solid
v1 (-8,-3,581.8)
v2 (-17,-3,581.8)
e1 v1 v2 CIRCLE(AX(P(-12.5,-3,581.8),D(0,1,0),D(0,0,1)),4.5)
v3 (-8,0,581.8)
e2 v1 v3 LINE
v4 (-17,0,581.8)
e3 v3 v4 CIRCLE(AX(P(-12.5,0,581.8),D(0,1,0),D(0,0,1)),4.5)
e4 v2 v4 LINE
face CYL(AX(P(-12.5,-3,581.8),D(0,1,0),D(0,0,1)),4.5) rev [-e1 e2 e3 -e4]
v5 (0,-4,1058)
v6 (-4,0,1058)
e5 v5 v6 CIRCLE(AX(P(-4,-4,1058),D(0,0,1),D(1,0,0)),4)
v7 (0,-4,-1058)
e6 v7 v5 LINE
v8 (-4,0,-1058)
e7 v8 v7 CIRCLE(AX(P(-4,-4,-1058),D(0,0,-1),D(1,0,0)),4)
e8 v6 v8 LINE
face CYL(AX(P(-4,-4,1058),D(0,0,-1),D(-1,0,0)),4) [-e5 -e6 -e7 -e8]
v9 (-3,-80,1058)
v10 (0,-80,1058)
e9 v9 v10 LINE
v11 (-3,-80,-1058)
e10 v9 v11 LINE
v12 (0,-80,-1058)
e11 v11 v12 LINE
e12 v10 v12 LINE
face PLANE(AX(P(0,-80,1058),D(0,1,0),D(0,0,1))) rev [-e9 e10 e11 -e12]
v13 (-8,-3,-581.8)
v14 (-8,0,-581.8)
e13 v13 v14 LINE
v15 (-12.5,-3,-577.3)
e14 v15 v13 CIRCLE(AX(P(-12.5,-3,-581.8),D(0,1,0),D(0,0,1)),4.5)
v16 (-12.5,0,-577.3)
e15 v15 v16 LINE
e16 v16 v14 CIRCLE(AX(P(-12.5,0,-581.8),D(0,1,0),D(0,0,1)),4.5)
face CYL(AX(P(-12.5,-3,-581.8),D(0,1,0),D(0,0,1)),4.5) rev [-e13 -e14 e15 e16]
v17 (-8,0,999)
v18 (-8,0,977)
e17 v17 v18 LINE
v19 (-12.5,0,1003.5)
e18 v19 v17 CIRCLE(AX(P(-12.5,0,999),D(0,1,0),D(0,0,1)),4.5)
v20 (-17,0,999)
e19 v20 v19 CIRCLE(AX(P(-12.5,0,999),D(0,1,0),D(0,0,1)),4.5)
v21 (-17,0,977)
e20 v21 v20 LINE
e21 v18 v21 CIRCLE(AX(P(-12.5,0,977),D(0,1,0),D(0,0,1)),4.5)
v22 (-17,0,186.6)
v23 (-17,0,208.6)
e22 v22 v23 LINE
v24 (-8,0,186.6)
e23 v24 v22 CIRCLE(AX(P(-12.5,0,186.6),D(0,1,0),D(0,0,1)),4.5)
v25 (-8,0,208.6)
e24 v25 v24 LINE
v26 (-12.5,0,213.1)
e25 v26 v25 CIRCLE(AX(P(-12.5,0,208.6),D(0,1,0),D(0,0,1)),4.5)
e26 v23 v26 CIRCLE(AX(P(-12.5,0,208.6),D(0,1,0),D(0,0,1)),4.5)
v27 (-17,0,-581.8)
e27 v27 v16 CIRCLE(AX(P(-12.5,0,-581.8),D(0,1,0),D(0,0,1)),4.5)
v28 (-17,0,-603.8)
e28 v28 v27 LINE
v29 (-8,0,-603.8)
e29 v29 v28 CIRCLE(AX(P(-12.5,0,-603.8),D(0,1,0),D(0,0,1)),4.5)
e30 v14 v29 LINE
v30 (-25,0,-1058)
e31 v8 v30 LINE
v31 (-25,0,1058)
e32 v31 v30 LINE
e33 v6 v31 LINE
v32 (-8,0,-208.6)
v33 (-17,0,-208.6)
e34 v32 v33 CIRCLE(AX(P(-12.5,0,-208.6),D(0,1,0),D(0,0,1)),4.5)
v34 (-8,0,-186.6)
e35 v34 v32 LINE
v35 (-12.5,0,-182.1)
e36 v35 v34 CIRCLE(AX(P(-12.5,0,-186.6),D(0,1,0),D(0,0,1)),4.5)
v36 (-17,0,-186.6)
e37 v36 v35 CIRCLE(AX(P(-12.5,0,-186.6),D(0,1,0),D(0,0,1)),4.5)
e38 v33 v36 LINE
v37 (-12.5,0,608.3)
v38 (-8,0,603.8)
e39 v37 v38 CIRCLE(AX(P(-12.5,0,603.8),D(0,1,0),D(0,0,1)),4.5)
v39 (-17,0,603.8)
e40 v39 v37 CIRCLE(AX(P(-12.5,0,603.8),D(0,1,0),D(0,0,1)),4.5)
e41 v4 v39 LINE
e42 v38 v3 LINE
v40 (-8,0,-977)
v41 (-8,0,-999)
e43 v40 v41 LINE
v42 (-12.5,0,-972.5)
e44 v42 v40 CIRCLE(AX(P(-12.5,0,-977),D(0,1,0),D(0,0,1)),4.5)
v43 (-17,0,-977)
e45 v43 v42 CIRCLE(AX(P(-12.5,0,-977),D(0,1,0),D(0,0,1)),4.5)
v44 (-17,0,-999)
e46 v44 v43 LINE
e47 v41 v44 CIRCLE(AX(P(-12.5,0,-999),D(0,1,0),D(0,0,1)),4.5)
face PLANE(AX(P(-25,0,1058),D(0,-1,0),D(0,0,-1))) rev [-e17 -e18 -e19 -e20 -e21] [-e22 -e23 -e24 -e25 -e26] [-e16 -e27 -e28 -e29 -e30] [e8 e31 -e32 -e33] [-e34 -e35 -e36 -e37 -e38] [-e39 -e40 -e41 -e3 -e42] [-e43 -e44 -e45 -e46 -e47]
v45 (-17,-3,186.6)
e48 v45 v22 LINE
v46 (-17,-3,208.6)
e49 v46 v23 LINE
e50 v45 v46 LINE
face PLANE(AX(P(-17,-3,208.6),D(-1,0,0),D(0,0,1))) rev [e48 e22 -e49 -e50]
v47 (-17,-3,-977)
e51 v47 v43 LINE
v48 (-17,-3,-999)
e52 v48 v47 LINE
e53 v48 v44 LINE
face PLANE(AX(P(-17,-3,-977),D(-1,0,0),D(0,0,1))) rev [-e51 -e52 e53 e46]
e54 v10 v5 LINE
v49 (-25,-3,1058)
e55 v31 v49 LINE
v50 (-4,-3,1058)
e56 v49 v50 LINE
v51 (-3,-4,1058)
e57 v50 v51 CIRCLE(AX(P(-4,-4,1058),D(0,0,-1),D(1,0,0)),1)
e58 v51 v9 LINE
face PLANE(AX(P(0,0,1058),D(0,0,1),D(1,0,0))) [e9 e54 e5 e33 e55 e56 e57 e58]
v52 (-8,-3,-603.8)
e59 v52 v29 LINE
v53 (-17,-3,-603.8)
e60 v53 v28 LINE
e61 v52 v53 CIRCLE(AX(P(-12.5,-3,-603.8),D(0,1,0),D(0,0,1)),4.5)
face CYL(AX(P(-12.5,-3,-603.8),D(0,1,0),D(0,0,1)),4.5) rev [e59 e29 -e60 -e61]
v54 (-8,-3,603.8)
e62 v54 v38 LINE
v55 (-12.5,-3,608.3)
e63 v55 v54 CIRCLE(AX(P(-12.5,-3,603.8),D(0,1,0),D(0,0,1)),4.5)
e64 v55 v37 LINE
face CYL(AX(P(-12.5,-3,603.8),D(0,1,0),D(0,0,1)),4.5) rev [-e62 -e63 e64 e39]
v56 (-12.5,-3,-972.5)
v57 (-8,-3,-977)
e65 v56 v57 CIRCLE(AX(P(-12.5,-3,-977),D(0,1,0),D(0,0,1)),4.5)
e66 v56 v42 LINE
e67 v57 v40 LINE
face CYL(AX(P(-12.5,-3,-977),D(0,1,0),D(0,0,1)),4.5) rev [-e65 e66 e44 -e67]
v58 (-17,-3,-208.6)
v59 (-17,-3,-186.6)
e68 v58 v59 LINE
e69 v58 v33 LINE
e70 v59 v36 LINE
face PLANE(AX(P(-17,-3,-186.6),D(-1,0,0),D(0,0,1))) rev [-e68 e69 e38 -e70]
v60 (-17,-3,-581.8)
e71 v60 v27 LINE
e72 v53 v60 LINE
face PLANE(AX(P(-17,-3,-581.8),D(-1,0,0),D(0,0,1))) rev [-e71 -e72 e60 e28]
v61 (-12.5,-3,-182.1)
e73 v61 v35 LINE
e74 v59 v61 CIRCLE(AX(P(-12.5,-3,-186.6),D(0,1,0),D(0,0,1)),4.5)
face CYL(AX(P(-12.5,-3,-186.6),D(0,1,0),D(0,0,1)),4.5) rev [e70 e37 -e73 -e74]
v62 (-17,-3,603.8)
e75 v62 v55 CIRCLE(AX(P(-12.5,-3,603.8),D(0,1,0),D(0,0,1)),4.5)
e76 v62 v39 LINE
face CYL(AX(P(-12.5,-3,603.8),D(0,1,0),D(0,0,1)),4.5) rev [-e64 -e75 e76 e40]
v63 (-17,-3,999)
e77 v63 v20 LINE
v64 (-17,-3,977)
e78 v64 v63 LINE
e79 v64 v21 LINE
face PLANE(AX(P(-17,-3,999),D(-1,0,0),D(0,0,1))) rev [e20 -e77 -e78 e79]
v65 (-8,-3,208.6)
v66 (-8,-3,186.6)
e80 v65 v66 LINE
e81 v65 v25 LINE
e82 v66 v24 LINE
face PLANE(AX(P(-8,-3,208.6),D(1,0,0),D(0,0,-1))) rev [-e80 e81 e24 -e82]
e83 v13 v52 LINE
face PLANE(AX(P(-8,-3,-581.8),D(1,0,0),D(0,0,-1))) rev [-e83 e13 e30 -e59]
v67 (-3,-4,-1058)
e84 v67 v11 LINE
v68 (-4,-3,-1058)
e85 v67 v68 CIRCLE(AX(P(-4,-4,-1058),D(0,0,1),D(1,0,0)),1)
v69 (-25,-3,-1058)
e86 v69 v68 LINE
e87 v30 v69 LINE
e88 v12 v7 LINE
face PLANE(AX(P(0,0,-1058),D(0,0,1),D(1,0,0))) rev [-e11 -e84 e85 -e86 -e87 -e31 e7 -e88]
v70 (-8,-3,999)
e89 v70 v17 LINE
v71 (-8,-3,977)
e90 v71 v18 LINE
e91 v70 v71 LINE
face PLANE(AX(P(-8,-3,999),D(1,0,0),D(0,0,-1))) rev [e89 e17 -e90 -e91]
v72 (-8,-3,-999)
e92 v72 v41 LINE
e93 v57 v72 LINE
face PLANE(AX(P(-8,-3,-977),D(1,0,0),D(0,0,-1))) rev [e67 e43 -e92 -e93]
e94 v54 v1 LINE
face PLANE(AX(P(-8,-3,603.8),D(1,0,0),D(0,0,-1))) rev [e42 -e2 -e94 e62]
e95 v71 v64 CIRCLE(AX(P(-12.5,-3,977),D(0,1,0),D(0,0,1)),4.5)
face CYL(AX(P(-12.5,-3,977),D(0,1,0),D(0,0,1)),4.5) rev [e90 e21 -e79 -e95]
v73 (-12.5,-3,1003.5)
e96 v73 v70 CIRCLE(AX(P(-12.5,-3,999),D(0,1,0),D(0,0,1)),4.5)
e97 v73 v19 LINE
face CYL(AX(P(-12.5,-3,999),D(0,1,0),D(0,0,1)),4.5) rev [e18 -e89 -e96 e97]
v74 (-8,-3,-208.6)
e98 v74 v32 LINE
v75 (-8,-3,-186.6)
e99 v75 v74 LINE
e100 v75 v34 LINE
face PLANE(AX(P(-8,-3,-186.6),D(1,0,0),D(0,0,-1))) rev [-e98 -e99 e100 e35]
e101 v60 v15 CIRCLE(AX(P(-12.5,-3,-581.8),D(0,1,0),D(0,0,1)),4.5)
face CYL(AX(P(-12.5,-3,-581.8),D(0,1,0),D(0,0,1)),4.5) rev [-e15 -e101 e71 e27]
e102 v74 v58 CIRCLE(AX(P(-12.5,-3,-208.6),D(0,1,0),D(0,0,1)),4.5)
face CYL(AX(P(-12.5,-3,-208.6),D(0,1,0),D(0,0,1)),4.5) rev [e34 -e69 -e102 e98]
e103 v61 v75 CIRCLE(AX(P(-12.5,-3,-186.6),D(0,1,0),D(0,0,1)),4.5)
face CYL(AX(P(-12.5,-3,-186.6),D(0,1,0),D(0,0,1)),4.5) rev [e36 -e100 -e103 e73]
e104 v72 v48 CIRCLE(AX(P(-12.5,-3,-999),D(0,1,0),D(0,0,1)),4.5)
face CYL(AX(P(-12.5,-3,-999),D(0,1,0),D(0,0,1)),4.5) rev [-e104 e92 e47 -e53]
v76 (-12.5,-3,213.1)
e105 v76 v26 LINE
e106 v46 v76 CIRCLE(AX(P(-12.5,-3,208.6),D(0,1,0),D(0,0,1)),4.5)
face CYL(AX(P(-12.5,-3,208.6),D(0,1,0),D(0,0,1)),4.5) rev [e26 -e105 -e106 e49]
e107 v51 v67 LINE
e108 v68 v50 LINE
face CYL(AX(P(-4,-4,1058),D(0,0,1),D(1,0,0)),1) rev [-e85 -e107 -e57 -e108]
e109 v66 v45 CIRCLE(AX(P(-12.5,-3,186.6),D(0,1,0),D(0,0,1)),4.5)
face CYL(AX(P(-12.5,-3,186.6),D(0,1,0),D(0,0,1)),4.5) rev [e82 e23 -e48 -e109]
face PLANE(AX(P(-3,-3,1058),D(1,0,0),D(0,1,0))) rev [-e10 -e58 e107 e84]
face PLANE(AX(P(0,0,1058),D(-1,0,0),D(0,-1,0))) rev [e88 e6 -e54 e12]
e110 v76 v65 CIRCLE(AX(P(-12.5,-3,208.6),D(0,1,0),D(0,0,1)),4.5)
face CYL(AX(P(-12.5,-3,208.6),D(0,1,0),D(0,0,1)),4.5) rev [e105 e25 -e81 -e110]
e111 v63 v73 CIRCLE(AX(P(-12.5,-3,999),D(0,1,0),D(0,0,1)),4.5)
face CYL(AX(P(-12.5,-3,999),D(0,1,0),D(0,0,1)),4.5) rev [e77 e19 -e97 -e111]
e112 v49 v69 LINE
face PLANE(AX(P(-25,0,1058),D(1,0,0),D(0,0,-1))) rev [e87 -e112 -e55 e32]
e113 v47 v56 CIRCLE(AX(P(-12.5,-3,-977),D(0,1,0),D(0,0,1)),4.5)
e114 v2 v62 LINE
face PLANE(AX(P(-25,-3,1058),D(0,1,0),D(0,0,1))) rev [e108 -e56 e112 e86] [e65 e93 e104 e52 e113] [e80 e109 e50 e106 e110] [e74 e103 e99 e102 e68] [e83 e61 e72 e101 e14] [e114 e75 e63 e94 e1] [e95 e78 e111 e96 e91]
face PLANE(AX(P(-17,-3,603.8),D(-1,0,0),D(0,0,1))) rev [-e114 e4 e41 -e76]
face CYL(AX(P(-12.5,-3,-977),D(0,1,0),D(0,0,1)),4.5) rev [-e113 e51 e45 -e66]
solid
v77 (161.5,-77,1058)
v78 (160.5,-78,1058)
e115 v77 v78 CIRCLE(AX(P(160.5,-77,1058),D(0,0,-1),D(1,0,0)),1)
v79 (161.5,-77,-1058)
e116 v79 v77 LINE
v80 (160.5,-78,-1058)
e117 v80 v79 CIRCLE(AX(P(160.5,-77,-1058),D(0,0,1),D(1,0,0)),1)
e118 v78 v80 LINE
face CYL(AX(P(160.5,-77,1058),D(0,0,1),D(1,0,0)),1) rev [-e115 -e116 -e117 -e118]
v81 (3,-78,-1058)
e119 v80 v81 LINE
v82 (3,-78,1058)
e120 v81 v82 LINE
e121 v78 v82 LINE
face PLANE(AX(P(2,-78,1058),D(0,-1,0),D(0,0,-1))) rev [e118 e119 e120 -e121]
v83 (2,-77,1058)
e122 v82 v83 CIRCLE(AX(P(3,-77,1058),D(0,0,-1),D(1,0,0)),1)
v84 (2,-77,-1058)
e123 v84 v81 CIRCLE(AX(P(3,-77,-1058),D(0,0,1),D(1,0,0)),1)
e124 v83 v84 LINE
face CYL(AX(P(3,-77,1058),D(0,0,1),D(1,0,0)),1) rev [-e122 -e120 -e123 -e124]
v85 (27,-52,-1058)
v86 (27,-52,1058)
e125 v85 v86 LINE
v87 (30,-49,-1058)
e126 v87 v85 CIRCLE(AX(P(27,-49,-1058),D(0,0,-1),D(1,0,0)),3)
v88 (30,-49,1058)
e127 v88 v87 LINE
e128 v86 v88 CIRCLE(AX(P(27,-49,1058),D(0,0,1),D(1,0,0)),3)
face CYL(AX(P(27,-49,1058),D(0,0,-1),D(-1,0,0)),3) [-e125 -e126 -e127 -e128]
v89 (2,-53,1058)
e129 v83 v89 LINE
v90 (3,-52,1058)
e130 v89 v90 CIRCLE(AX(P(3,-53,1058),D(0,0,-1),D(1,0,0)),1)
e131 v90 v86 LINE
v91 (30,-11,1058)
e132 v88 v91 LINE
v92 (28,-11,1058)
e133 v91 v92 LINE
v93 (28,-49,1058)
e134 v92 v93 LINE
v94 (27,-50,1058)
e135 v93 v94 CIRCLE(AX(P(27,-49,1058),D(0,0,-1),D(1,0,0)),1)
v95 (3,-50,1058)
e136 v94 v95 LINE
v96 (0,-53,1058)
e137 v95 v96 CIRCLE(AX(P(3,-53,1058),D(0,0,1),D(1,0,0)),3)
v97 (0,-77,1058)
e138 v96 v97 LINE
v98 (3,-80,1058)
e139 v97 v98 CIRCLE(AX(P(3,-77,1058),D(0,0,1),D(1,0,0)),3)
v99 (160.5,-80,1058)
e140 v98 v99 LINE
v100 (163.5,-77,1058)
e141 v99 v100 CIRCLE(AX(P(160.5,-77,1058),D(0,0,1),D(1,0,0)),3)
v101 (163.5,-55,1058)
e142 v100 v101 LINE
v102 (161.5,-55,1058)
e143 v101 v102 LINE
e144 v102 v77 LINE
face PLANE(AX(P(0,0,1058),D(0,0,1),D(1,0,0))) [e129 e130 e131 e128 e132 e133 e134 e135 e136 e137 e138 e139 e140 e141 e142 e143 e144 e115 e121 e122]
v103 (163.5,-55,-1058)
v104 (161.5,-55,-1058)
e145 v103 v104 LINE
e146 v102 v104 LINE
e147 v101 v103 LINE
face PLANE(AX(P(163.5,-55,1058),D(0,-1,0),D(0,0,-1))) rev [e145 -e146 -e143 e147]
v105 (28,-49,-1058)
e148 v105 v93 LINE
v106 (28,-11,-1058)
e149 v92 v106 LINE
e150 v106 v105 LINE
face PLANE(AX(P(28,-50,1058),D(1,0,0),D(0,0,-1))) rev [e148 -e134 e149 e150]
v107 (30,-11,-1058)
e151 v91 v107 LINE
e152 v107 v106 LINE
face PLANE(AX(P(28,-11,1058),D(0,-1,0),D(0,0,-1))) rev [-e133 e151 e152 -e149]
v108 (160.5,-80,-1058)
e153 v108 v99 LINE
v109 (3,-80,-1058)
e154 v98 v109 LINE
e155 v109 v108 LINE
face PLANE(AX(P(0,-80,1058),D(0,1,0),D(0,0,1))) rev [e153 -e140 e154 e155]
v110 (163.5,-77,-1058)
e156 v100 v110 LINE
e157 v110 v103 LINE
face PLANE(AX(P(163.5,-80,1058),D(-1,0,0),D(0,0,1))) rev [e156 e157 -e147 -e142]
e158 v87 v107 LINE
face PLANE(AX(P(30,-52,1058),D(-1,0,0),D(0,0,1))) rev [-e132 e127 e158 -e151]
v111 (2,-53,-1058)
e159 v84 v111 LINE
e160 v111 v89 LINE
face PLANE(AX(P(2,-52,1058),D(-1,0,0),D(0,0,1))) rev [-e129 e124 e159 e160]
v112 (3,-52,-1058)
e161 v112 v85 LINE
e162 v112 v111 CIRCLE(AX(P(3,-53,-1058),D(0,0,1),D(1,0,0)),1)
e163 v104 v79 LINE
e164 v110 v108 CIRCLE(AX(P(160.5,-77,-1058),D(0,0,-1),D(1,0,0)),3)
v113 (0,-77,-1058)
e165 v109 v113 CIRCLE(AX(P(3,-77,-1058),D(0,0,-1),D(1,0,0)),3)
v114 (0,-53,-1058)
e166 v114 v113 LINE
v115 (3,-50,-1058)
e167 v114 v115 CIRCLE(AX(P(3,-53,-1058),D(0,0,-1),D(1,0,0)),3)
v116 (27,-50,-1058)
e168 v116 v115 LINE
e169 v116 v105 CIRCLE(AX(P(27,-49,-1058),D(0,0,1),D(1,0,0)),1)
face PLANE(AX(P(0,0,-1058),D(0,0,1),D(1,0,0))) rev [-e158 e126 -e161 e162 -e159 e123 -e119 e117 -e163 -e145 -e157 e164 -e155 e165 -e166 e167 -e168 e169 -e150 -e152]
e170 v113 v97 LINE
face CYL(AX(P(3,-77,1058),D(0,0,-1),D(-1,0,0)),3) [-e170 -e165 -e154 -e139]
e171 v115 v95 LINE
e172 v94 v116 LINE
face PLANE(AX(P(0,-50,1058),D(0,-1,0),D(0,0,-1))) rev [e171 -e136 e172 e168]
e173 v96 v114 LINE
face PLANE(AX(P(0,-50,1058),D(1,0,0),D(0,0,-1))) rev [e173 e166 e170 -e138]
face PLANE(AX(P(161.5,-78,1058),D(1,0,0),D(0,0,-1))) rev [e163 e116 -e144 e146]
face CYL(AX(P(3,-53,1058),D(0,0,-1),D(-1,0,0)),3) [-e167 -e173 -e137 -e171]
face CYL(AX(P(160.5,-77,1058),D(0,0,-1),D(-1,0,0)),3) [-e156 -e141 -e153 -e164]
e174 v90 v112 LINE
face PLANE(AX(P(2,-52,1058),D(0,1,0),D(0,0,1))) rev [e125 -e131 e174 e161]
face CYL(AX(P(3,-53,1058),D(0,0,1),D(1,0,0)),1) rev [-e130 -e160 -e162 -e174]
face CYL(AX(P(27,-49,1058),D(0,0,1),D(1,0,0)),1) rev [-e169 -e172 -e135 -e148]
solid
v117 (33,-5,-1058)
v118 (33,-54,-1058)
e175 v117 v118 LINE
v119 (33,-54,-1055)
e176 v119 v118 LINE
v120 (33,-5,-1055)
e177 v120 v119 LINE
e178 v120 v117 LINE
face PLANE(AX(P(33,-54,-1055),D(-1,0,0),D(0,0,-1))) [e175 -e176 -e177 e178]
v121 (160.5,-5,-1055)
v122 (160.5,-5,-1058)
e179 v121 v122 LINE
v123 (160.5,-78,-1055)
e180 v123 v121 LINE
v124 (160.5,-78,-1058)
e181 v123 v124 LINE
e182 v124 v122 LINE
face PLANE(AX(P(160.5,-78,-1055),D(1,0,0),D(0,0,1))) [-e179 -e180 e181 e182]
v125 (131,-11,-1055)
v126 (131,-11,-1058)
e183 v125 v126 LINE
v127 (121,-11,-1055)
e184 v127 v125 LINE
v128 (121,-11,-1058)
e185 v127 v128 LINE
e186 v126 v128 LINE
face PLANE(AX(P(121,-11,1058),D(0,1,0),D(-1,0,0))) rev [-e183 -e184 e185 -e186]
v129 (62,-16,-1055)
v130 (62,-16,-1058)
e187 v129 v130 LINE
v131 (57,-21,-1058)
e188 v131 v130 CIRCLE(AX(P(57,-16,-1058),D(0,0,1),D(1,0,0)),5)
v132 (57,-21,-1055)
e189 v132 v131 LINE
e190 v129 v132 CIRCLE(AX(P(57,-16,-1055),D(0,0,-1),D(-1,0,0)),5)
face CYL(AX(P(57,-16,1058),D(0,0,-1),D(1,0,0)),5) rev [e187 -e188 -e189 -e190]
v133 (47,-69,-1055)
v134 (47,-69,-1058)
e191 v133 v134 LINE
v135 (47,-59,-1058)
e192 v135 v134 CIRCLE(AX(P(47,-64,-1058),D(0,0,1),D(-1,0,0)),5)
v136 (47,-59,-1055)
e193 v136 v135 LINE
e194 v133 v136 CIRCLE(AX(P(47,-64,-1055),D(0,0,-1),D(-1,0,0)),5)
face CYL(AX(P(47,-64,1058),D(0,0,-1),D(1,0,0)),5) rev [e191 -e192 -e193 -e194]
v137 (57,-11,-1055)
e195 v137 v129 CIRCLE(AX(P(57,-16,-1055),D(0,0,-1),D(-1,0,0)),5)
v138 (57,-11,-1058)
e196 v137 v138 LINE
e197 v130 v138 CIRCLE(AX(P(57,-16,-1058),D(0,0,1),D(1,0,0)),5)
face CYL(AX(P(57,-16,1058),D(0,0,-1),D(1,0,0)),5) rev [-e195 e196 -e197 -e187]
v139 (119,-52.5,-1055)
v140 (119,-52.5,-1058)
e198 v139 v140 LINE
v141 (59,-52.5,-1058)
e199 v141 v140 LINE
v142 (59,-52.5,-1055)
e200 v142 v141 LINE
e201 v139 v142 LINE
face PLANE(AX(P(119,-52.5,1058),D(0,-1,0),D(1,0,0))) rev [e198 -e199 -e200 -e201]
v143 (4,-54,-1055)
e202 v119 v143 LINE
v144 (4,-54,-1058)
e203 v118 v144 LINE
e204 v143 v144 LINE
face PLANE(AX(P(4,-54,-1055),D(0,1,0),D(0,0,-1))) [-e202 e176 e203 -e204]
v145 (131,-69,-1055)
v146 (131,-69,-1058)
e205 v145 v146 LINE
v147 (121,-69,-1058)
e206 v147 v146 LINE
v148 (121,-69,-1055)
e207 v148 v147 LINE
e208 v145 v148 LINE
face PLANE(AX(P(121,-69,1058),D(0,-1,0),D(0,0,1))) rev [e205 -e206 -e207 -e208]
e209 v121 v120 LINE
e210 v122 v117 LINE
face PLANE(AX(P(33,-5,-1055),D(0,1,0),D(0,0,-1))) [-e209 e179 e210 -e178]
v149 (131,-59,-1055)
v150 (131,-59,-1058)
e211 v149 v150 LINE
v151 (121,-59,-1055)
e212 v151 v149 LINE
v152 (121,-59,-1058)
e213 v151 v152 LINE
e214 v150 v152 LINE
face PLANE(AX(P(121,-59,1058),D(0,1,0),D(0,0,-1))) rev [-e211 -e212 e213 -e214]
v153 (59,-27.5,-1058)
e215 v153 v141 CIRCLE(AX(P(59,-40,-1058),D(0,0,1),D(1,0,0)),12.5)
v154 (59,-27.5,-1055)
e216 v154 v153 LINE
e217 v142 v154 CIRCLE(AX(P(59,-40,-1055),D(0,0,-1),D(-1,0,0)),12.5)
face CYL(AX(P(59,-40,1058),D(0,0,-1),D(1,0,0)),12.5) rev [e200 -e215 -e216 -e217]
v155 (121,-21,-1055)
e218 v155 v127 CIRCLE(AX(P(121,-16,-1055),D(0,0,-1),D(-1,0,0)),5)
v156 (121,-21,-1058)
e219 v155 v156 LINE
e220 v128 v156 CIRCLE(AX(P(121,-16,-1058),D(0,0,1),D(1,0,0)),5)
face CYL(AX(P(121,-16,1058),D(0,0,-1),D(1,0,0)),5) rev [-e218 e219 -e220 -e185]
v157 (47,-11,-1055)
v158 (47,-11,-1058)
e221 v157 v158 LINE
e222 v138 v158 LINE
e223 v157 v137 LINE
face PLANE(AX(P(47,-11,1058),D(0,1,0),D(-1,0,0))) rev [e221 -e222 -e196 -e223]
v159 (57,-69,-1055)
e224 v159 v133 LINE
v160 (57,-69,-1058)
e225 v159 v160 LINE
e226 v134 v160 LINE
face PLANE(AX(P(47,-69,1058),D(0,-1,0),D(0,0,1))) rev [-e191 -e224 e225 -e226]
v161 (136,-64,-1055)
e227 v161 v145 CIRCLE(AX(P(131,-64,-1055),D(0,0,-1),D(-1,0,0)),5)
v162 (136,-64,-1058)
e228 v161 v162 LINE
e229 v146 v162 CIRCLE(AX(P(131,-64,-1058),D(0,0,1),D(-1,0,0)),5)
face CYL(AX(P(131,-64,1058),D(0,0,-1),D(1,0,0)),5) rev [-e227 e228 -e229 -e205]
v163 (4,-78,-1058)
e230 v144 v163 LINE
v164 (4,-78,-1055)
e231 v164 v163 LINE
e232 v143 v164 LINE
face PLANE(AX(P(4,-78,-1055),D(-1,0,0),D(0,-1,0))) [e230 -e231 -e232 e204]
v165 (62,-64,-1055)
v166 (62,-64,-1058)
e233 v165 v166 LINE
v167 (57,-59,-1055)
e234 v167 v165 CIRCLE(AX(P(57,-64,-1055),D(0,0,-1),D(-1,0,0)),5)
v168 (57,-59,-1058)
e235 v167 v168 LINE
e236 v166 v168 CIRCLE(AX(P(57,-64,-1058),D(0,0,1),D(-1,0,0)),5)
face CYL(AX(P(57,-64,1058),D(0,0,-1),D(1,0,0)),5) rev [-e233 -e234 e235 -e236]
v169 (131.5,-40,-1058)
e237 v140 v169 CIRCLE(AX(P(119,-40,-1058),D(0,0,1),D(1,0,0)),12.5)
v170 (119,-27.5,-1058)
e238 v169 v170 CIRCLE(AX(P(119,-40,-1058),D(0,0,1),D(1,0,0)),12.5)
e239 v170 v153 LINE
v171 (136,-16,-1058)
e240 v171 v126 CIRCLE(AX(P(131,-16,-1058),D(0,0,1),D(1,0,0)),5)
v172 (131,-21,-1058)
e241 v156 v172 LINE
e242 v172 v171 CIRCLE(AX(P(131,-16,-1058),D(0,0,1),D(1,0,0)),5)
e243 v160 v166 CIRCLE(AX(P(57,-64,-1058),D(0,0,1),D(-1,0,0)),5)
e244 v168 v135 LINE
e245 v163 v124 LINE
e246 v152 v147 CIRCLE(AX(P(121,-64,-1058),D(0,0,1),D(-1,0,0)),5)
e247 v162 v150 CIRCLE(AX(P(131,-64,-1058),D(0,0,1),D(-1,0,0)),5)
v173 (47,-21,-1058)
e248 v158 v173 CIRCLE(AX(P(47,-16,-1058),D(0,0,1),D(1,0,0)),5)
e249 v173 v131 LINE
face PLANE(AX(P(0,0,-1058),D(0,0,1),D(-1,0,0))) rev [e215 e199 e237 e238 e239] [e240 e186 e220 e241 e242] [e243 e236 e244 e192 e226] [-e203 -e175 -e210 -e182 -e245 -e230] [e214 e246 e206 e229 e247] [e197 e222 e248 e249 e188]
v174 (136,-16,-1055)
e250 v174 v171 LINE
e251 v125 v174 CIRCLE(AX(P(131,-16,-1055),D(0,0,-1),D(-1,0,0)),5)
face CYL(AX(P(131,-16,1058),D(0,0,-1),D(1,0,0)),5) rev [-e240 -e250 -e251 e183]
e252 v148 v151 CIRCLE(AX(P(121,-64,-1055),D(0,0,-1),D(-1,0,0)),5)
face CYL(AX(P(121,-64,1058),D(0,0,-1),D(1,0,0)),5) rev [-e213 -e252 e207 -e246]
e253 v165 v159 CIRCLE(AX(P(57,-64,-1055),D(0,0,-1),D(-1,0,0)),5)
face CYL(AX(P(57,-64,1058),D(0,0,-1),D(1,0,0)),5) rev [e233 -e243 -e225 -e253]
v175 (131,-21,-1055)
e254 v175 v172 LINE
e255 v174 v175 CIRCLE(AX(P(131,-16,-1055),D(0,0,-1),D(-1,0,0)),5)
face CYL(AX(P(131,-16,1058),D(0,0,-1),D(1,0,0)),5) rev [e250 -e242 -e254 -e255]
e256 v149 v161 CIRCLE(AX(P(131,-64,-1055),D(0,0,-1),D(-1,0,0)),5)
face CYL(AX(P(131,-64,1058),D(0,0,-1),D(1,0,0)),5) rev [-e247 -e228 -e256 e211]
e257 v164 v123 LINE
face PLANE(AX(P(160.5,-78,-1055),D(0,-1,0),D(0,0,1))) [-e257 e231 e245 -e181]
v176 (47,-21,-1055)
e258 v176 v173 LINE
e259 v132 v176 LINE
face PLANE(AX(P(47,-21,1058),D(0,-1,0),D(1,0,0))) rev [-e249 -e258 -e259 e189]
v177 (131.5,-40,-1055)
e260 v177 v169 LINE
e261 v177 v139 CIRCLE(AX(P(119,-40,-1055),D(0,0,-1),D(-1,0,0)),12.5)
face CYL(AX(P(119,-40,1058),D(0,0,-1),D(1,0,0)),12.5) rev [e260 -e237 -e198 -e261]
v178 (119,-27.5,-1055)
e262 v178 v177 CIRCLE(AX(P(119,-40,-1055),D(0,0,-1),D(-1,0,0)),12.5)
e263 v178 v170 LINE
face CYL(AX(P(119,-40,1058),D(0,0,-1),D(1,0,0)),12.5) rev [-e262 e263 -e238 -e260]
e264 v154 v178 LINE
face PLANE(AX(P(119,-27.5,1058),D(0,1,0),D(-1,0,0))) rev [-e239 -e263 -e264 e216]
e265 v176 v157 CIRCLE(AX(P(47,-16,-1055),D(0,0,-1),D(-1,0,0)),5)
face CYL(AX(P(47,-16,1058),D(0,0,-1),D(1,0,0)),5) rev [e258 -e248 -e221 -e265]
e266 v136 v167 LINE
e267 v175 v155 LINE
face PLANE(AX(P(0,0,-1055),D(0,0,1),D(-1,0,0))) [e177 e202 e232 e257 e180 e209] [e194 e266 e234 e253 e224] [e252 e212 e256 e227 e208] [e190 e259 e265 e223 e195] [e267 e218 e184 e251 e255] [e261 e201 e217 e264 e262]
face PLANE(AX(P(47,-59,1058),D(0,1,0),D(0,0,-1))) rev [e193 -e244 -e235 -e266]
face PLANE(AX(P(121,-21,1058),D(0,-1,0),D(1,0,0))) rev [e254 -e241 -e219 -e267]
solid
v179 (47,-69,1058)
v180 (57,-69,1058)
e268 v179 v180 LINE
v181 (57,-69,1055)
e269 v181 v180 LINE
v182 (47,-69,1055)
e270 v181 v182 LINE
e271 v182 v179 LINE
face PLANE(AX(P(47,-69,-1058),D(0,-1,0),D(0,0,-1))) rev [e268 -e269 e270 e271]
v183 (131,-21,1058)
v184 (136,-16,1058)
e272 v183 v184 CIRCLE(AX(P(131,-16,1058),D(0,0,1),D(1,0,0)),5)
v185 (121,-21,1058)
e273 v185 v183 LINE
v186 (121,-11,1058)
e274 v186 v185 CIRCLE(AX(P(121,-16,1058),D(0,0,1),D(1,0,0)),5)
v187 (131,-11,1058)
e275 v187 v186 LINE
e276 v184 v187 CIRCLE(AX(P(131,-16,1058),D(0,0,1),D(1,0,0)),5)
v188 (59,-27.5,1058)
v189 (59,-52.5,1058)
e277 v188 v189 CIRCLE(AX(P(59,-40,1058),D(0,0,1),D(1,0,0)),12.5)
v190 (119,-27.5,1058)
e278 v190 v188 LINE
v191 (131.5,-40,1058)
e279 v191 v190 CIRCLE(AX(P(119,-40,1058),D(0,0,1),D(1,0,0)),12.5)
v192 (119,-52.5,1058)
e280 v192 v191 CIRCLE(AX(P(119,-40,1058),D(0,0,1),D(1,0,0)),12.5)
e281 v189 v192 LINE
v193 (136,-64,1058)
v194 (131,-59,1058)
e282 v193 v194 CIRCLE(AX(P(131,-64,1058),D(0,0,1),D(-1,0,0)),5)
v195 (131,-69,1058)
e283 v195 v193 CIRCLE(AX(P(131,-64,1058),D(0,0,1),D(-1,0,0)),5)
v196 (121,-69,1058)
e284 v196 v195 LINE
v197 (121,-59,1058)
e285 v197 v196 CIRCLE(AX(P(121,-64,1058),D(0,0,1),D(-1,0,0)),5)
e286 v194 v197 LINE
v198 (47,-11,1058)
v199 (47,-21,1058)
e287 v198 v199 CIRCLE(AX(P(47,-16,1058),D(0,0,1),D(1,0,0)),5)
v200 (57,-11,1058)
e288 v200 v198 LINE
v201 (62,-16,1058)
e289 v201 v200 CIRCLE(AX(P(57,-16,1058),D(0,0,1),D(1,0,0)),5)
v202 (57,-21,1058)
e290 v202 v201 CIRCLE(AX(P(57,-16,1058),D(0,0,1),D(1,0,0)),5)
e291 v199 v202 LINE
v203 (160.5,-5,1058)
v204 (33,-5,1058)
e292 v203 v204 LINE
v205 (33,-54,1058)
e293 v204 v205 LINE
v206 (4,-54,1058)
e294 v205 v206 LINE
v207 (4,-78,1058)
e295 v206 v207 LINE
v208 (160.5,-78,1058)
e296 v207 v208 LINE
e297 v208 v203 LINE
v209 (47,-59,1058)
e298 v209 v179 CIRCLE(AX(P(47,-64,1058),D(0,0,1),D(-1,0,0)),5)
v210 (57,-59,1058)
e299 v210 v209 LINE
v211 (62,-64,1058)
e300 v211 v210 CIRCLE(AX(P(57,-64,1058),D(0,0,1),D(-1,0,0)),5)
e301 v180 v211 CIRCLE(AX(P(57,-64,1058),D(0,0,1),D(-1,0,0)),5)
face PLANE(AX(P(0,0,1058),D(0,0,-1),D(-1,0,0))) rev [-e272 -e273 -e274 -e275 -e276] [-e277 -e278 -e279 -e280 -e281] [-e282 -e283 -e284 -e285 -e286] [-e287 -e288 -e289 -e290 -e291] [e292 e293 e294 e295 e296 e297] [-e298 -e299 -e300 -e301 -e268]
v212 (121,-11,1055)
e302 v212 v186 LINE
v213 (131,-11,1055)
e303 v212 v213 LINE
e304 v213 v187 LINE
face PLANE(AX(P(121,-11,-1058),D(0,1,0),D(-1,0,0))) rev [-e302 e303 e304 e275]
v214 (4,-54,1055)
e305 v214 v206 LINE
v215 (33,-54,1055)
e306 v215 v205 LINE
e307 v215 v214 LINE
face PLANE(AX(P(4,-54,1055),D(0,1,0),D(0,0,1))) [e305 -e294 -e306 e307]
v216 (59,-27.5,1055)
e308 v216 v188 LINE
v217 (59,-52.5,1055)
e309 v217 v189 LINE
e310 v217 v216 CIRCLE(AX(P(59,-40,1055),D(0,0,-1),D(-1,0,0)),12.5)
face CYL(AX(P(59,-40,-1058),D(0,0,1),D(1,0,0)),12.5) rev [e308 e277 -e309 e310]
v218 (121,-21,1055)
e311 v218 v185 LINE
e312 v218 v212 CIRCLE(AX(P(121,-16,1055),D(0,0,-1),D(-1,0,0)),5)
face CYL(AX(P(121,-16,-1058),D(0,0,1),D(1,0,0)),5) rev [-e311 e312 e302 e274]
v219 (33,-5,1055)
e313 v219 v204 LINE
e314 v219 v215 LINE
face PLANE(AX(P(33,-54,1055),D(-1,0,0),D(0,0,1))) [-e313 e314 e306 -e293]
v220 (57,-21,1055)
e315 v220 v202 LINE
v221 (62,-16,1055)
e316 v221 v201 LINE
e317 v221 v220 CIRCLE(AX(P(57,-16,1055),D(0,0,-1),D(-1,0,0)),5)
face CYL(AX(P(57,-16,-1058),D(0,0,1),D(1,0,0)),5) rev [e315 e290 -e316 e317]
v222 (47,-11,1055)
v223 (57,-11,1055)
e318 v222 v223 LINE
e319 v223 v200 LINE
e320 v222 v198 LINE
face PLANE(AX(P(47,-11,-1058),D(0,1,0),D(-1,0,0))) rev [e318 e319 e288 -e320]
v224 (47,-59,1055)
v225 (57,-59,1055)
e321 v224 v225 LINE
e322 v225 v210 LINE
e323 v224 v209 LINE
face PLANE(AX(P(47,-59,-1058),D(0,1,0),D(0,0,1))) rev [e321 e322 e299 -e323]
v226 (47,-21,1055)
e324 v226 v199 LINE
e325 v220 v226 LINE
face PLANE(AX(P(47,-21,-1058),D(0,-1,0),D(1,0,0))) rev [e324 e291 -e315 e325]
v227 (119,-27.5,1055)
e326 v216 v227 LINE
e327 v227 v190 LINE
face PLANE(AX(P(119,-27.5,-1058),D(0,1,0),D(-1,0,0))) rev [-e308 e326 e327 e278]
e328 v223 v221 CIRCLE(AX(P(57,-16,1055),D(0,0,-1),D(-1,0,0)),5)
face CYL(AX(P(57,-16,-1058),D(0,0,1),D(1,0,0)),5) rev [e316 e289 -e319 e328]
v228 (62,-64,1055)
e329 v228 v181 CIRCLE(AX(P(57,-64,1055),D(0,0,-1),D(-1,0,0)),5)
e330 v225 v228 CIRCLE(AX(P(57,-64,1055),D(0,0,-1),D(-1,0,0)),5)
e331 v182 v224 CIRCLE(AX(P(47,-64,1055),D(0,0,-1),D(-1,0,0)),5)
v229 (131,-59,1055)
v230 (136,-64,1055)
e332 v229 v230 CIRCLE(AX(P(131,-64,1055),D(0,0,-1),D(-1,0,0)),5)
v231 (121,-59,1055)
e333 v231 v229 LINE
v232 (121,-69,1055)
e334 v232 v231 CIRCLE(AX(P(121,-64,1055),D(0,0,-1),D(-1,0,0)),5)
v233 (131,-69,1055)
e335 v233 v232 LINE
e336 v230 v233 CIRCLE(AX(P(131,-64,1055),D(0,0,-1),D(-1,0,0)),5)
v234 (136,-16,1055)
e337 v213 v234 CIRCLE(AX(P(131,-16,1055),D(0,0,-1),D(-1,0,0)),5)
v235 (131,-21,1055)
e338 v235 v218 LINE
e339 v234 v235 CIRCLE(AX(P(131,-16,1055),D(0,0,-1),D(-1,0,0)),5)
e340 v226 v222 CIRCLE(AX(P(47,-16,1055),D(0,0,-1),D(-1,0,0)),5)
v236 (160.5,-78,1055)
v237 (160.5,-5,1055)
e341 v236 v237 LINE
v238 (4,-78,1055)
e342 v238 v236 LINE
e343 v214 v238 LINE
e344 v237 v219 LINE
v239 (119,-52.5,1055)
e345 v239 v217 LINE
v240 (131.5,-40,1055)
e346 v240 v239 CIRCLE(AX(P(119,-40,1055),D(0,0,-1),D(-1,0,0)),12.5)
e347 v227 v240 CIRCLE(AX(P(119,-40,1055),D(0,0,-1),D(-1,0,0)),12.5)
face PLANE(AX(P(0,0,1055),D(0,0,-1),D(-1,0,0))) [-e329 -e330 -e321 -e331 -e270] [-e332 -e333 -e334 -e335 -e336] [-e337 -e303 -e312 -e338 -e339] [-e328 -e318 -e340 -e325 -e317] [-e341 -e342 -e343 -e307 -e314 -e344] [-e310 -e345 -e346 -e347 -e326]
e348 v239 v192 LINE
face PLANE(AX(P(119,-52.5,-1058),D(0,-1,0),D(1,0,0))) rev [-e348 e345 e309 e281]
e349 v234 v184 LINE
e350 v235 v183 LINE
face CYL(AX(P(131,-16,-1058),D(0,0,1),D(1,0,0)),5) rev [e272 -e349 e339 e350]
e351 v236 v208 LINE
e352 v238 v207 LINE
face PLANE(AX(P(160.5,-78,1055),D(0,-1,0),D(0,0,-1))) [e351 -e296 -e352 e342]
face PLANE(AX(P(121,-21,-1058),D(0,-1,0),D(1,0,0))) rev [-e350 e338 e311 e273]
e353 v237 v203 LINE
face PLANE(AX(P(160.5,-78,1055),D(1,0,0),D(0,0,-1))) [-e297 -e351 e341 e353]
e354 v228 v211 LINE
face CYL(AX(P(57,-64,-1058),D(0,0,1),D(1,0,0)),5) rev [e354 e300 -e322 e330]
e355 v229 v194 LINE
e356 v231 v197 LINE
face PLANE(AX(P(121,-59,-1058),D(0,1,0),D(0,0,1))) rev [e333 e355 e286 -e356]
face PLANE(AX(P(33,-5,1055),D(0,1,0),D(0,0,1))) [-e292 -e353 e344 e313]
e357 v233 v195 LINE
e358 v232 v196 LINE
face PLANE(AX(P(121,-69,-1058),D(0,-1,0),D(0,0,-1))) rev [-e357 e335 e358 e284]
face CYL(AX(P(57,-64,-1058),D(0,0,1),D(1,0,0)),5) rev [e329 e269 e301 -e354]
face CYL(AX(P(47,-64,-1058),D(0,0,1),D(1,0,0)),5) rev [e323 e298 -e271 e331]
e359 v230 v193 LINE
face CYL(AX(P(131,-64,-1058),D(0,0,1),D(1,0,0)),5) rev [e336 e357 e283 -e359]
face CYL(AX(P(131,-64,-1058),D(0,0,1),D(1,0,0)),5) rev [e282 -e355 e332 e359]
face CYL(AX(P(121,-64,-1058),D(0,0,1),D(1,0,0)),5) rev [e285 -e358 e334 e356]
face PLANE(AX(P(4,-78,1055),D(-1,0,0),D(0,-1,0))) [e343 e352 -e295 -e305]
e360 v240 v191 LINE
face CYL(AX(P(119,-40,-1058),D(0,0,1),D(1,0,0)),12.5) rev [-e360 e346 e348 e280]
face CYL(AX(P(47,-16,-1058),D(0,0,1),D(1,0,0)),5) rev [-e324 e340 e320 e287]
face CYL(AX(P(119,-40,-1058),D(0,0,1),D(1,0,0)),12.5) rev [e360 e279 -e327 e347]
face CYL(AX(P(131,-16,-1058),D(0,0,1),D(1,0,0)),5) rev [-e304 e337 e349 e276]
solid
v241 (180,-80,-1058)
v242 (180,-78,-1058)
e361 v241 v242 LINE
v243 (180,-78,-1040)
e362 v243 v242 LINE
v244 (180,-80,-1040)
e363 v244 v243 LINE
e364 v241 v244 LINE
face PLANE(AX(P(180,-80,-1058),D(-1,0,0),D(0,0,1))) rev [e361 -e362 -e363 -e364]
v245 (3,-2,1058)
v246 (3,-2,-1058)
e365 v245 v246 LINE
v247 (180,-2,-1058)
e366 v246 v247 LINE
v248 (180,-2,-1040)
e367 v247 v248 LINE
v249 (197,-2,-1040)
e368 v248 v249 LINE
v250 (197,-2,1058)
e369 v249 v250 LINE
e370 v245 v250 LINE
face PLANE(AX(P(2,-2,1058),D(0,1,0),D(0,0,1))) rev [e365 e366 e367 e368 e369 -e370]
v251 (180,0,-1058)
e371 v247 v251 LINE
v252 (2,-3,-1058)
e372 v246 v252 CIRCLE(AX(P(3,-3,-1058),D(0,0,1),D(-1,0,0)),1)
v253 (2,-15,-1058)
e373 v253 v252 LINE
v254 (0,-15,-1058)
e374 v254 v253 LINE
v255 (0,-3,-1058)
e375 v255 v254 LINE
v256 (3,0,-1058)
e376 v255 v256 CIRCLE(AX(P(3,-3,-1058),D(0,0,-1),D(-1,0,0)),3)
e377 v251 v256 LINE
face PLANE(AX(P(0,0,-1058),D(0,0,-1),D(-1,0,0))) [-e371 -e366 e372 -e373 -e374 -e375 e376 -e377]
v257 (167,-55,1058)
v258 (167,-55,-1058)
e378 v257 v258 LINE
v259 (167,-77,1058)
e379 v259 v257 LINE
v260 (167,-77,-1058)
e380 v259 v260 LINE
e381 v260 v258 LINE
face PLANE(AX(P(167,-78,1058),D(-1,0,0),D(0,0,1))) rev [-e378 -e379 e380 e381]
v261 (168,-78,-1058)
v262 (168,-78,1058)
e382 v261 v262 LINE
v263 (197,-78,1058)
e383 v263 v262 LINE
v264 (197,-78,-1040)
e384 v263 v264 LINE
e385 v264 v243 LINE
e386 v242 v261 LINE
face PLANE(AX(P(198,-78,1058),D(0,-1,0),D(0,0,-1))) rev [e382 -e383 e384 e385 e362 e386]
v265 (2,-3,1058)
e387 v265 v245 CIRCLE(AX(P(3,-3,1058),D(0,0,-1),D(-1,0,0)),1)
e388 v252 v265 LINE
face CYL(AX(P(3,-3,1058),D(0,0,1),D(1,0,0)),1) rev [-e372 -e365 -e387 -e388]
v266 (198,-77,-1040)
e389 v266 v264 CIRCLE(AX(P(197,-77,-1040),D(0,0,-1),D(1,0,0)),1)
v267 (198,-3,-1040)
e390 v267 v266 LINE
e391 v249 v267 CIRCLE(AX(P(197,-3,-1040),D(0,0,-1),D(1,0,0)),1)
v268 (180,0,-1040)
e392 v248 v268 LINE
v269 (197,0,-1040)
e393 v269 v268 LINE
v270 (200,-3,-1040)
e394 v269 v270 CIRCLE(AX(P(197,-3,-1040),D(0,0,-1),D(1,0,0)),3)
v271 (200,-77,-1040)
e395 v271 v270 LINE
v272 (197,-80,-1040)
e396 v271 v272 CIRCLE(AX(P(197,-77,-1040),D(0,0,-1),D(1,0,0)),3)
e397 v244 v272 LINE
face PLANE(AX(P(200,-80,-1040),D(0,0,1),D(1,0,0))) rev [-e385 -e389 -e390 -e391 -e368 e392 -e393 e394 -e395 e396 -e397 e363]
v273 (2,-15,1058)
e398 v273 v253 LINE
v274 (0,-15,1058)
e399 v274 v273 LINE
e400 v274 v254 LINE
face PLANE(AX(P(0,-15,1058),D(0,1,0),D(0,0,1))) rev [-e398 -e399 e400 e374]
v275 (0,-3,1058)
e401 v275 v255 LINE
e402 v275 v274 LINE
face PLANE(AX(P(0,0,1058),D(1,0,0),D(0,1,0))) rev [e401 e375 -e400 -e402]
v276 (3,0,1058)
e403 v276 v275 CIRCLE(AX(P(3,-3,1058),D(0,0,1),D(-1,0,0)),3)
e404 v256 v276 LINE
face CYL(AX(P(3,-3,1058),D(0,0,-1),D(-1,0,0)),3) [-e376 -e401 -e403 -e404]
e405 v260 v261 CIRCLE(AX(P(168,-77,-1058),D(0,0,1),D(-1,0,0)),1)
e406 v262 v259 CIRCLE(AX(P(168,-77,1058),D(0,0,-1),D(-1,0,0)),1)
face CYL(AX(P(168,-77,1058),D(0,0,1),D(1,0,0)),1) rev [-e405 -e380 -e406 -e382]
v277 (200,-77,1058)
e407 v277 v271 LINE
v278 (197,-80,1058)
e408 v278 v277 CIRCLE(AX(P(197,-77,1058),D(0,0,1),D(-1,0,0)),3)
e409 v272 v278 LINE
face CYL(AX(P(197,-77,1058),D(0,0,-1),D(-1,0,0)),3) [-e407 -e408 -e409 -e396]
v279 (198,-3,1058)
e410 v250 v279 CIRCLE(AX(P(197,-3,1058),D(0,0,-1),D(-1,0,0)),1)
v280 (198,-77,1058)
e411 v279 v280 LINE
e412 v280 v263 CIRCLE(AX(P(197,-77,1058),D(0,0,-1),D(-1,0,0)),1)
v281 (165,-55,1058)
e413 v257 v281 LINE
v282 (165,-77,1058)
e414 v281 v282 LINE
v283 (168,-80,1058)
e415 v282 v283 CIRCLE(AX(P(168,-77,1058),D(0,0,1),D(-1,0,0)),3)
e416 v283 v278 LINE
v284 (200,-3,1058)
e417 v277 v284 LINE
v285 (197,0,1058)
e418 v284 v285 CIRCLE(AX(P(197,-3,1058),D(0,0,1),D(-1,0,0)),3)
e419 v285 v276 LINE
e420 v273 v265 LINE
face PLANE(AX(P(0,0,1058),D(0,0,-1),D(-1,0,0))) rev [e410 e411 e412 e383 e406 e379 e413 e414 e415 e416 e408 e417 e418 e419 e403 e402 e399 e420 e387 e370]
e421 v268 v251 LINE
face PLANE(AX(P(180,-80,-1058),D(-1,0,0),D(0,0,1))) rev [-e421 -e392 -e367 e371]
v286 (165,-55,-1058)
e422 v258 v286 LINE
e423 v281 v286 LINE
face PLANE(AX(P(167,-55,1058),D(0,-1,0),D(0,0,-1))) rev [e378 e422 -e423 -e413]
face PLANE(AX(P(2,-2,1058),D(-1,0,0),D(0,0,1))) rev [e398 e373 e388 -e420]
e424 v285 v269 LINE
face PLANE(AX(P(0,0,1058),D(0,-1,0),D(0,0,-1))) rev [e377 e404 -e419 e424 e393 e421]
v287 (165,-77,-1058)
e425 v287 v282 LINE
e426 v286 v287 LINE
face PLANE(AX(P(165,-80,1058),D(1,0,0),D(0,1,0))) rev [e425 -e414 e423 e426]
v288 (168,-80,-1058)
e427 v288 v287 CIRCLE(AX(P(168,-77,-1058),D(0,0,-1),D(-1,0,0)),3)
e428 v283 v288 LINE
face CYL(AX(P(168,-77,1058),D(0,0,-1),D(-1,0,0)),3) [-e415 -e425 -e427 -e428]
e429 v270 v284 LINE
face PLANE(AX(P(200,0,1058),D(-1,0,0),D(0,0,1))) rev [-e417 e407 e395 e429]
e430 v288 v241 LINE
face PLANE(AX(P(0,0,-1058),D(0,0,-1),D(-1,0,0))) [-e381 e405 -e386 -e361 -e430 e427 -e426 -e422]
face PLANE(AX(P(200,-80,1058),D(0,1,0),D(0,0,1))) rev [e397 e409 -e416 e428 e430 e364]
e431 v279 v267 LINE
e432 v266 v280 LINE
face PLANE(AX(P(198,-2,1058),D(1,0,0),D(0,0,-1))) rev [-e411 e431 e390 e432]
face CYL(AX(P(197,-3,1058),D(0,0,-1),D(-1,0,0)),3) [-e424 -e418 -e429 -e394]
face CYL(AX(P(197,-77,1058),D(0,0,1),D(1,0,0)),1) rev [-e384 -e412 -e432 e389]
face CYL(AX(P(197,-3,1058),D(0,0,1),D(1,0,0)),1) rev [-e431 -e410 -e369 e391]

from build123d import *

# Parameters (mm, degrees)
EXTRUDE_1_DEPTH             = 1058
EXTRUDE_2_DEPTH             = 1058
EXTRUDE_2_2_DEPTH           = 1058
EXTRUDE_3_DEPTH             = 3
FILLET_1_R                  = 4
FILLET_2_R                  = 1
FILLET_3_R                  = 1
FILLET_4_R                  = 1
FILLET_5_R                  = 3
FILLET_6_R                  = 3
CUT_EXTRUDE_1_DEPTH         = 2127.935824138
CUT_EXTRUDE_3490_DEPTH      = 3
CUT_EXTRUDE_3711_DEPTH      = 1080.705515407
CUT_EXTRUDE_3711_DEPTH_BACK = 1080.705515407
SKETCH_6_W                  = 20
SKETCH_6_H                  = 18


with BuildPart() as part:
    # 草图1 → 凸台-拉伸1 (new, symmetric)
    with BuildSketch(Plane.XY):
        Polygon((-25, 0), (0, 0), (0, -80), (-3, -80), (-3, -3), (-25, -3), align=None)
    extrude(amount=EXTRUDE_1_DEPTH, both=True)

    # 圆角1
    fillet_1_edges = [part.edges().sort_by_distance(p)[0] for p in [
        (0, 0, 0),
    ]]
    fillet(fillet_1_edges, radius=FILLET_1_R)

    # 圆角2
    fillet_2_edges = [part.edges().sort_by_distance(p)[0] for p in [
        (-3, -3, 0),
    ]]
    fillet(fillet_2_edges, radius=FILLET_2_R)

    # 草图7 → Cut-Extrude 3490 (cut)
    with BuildSketch(Plane(origin=(0, 0, 0), x_dir=(1, 0, 0), z_dir=(0, 1, 0))):
        with BuildLine():
            Line((-17, 977), (-17, 999))
            ThreePointArc((-17, 999), (-12.5, 1003.5), (-8, 999))
            Line((-8, 999), (-8, 977))
            ThreePointArc((-8, 977), (-12.5, 972.5), (-17, 977))
        make_face()
        with BuildLine():
            Line((-17, 581.8), (-17, 603.8))
            ThreePointArc((-17, 603.8), (-12.5, 608.3), (-8, 603.8))
            Line((-8, 603.8), (-8, 581.8))
            ThreePointArc((-8, 581.8), (-12.5, 577.3), (-17, 581.8))
        make_face()
        with BuildLine():
            Line((-17, 186.6), (-17, 208.6))
            ThreePointArc((-17, 208.6), (-12.5, 213.1), (-8, 208.6))
            Line((-8, 208.6), (-8, 186.6))
            ThreePointArc((-8, 186.6), (-12.5, 182.1), (-17, 186.6))
        make_face()
        with BuildLine():
            Line((-17, -208.6), (-17, -186.6))
            ThreePointArc((-17, -186.6), (-12.5, -182.1), (-8, -186.6))
            Line((-8, -186.6), (-8, -208.6))
            ThreePointArc((-8, -208.6), (-12.5, -213.1), (-17, -208.6))
        make_face()
        with BuildLine():
            Line((-17, -603.8), (-17, -581.8))
            ThreePointArc((-17, -581.8), (-12.5, -577.3), (-8, -581.8))
            Line((-8, -581.8), (-8, -603.8))
            ThreePointArc((-8, -603.8), (-12.5, -608.3), (-17, -603.8))
        make_face()
        with BuildLine():
            Line((-17, -999), (-17, -977))
            ThreePointArc((-17, -977), (-12.5, -972.5), (-8, -977))
            Line((-8, -977), (-8, -999))
            ThreePointArc((-8, -999), (-12.5, -1003.5), (-17, -999))
        make_face()
    extrude(amount=-CUT_EXTRUDE_3490_DEPTH, mode=Mode.SUBTRACT)


with BuildPart() as body_2:
    # 草图2 → 凸台-拉伸2 (new, symmetric)
    with BuildSketch(Plane.XY):
        Polygon((0, 0), (0, -15), (2, -15), (2, -2), (198, -2), (198, -78), (167, -78), (167, -55), (165, -55), (165, -80), (200, -80), (200, 0), align=None)
    extrude(amount=EXTRUDE_2_DEPTH, both=True)

    # 圆角3
    fillet_3_edges = [body_2.edges().sort_by_distance(p)[0] for p in [
        (167, -78, 0),
        (198, -78, 0),
        (198, -2, 0),
        (2, -2, 0),
    ]]
    fillet(fillet_3_edges, radius=FILLET_3_R)

    # 圆角5
    fillet_5_edges = [body_2.edges().sort_by_distance(p)[0] for p in [
        (200, 0, 0),
        (200, -80, 0),
        (165, -80, 0),
        (0, 0, 0),
    ]]
    fillet(fillet_5_edges, radius=FILLET_5_R)

    # 草图6 → Cut-Extrude 3711 (cut, two sides: drawn at the far end of the back side and taken through both)
    with BuildSketch(Plane(origin=(0, 0, 0), x_dir=(1, 0, 0), z_dir=(0, 1, 0)).offset(-CUT_EXTRUDE_3711_DEPTH_BACK)):
        with Locations((190, 1049)):
            Rectangle(SKETCH_6_W, SKETCH_6_H)
    extrude(amount=CUT_EXTRUDE_3711_DEPTH + CUT_EXTRUDE_3711_DEPTH_BACK, mode=Mode.SUBTRACT)


with BuildPart() as body_3:
    # 草图2 → Extrude 2 2 (new, symmetric)
    with BuildSketch(Plane.XY):
        Polygon((0, -50), (0, -80), (163.5, -80), (163.5, -55), (161.5, -55), (161.5, -78), (2, -78), (2, -52), (30, -52), (30, -11), (28, -11), (28, -50), align=None)
    extrude(amount=EXTRUDE_2_2_DEPTH, both=True)

    # 圆角4
    fillet_4_edges = [body_3.edges().sort_by_distance(p)[0] for p in [
        (28, -50, 0),
        (2, -52, 0),
        (2, -78, 0),
        (161.5, -78, 0),
    ]]
    fillet(fillet_4_edges, radius=FILLET_4_R)

    # 圆角6
    fillet_6_edges = [body_3.edges().sort_by_distance(p)[0] for p in [
        (30, -52, 0),
        (163.5, -80, 0),
        (0, -80, 0),
        (0, -50, 0),
    ]]
    fillet(fillet_6_edges, radius=FILLET_6_R)


with BuildPart() as body_4:
    # 草图3 → 凸台-拉伸3 (new body)
    with BuildSketch(Plane.XY.offset(1058)):
        Polygon((160.5, -78), (160.5, -5), (33, -5), (33, -54), (4, -54), (4, -78), align=None)
    extrude(amount=-EXTRUDE_3_DEPTH)

    # 草图5 → 切除-拉伸1 (cut, through all)
    with BuildSketch(Plane.XY.offset(1058)):
        with BuildLine():
            Line((47, -11), (57, -11))
            ThreePointArc((57, -11), (62, -16), (57, -21))
            Line((57, -21), (47, -21))
            ThreePointArc((47, -21), (42, -16), (47, -11))
        make_face()
        with BuildLine():
            Line((47, -69), (57, -69))
            ThreePointArc((57, -69), (62, -64), (57, -59))
            Line((57, -59), (47, -59))
            ThreePointArc((47, -59), (42, -64), (47, -69))
        make_face()
        with BuildLine():
            Line((121, -11), (131, -11))
            ThreePointArc((131, -11), (136, -16), (131, -21))
            Line((131, -21), (121, -21))
            ThreePointArc((121, -21), (116, -16), (121, -11))
        make_face()
        with BuildLine():
            Line((121, -69), (131, -69))
            ThreePointArc((131, -69), (136, -64), (131, -59))
            Line((131, -59), (121, -59))
            ThreePointArc((121, -59), (116, -64), (121, -69))
        make_face()
        with BuildLine():
            Line((119, -52.5), (59, -52.5))
            ThreePointArc((59, -52.5), (46.5, -40), (59, -27.5))
            Line((59, -27.5), (119, -27.5))
            ThreePointArc((119, -27.5), (131.5, -40), (119, -52.5))
        make_face()
    extrude(amount=-CUT_EXTRUDE_1_DEPTH, mode=Mode.SUBTRACT)


with BuildPart() as body_5:
    # 镜向1: mirrored copy
    add(body_4.part.mirror(Plane.XY))


solid = Compound([part.part, body_2.part, body_3.part, body_4.part, body_5.part])
